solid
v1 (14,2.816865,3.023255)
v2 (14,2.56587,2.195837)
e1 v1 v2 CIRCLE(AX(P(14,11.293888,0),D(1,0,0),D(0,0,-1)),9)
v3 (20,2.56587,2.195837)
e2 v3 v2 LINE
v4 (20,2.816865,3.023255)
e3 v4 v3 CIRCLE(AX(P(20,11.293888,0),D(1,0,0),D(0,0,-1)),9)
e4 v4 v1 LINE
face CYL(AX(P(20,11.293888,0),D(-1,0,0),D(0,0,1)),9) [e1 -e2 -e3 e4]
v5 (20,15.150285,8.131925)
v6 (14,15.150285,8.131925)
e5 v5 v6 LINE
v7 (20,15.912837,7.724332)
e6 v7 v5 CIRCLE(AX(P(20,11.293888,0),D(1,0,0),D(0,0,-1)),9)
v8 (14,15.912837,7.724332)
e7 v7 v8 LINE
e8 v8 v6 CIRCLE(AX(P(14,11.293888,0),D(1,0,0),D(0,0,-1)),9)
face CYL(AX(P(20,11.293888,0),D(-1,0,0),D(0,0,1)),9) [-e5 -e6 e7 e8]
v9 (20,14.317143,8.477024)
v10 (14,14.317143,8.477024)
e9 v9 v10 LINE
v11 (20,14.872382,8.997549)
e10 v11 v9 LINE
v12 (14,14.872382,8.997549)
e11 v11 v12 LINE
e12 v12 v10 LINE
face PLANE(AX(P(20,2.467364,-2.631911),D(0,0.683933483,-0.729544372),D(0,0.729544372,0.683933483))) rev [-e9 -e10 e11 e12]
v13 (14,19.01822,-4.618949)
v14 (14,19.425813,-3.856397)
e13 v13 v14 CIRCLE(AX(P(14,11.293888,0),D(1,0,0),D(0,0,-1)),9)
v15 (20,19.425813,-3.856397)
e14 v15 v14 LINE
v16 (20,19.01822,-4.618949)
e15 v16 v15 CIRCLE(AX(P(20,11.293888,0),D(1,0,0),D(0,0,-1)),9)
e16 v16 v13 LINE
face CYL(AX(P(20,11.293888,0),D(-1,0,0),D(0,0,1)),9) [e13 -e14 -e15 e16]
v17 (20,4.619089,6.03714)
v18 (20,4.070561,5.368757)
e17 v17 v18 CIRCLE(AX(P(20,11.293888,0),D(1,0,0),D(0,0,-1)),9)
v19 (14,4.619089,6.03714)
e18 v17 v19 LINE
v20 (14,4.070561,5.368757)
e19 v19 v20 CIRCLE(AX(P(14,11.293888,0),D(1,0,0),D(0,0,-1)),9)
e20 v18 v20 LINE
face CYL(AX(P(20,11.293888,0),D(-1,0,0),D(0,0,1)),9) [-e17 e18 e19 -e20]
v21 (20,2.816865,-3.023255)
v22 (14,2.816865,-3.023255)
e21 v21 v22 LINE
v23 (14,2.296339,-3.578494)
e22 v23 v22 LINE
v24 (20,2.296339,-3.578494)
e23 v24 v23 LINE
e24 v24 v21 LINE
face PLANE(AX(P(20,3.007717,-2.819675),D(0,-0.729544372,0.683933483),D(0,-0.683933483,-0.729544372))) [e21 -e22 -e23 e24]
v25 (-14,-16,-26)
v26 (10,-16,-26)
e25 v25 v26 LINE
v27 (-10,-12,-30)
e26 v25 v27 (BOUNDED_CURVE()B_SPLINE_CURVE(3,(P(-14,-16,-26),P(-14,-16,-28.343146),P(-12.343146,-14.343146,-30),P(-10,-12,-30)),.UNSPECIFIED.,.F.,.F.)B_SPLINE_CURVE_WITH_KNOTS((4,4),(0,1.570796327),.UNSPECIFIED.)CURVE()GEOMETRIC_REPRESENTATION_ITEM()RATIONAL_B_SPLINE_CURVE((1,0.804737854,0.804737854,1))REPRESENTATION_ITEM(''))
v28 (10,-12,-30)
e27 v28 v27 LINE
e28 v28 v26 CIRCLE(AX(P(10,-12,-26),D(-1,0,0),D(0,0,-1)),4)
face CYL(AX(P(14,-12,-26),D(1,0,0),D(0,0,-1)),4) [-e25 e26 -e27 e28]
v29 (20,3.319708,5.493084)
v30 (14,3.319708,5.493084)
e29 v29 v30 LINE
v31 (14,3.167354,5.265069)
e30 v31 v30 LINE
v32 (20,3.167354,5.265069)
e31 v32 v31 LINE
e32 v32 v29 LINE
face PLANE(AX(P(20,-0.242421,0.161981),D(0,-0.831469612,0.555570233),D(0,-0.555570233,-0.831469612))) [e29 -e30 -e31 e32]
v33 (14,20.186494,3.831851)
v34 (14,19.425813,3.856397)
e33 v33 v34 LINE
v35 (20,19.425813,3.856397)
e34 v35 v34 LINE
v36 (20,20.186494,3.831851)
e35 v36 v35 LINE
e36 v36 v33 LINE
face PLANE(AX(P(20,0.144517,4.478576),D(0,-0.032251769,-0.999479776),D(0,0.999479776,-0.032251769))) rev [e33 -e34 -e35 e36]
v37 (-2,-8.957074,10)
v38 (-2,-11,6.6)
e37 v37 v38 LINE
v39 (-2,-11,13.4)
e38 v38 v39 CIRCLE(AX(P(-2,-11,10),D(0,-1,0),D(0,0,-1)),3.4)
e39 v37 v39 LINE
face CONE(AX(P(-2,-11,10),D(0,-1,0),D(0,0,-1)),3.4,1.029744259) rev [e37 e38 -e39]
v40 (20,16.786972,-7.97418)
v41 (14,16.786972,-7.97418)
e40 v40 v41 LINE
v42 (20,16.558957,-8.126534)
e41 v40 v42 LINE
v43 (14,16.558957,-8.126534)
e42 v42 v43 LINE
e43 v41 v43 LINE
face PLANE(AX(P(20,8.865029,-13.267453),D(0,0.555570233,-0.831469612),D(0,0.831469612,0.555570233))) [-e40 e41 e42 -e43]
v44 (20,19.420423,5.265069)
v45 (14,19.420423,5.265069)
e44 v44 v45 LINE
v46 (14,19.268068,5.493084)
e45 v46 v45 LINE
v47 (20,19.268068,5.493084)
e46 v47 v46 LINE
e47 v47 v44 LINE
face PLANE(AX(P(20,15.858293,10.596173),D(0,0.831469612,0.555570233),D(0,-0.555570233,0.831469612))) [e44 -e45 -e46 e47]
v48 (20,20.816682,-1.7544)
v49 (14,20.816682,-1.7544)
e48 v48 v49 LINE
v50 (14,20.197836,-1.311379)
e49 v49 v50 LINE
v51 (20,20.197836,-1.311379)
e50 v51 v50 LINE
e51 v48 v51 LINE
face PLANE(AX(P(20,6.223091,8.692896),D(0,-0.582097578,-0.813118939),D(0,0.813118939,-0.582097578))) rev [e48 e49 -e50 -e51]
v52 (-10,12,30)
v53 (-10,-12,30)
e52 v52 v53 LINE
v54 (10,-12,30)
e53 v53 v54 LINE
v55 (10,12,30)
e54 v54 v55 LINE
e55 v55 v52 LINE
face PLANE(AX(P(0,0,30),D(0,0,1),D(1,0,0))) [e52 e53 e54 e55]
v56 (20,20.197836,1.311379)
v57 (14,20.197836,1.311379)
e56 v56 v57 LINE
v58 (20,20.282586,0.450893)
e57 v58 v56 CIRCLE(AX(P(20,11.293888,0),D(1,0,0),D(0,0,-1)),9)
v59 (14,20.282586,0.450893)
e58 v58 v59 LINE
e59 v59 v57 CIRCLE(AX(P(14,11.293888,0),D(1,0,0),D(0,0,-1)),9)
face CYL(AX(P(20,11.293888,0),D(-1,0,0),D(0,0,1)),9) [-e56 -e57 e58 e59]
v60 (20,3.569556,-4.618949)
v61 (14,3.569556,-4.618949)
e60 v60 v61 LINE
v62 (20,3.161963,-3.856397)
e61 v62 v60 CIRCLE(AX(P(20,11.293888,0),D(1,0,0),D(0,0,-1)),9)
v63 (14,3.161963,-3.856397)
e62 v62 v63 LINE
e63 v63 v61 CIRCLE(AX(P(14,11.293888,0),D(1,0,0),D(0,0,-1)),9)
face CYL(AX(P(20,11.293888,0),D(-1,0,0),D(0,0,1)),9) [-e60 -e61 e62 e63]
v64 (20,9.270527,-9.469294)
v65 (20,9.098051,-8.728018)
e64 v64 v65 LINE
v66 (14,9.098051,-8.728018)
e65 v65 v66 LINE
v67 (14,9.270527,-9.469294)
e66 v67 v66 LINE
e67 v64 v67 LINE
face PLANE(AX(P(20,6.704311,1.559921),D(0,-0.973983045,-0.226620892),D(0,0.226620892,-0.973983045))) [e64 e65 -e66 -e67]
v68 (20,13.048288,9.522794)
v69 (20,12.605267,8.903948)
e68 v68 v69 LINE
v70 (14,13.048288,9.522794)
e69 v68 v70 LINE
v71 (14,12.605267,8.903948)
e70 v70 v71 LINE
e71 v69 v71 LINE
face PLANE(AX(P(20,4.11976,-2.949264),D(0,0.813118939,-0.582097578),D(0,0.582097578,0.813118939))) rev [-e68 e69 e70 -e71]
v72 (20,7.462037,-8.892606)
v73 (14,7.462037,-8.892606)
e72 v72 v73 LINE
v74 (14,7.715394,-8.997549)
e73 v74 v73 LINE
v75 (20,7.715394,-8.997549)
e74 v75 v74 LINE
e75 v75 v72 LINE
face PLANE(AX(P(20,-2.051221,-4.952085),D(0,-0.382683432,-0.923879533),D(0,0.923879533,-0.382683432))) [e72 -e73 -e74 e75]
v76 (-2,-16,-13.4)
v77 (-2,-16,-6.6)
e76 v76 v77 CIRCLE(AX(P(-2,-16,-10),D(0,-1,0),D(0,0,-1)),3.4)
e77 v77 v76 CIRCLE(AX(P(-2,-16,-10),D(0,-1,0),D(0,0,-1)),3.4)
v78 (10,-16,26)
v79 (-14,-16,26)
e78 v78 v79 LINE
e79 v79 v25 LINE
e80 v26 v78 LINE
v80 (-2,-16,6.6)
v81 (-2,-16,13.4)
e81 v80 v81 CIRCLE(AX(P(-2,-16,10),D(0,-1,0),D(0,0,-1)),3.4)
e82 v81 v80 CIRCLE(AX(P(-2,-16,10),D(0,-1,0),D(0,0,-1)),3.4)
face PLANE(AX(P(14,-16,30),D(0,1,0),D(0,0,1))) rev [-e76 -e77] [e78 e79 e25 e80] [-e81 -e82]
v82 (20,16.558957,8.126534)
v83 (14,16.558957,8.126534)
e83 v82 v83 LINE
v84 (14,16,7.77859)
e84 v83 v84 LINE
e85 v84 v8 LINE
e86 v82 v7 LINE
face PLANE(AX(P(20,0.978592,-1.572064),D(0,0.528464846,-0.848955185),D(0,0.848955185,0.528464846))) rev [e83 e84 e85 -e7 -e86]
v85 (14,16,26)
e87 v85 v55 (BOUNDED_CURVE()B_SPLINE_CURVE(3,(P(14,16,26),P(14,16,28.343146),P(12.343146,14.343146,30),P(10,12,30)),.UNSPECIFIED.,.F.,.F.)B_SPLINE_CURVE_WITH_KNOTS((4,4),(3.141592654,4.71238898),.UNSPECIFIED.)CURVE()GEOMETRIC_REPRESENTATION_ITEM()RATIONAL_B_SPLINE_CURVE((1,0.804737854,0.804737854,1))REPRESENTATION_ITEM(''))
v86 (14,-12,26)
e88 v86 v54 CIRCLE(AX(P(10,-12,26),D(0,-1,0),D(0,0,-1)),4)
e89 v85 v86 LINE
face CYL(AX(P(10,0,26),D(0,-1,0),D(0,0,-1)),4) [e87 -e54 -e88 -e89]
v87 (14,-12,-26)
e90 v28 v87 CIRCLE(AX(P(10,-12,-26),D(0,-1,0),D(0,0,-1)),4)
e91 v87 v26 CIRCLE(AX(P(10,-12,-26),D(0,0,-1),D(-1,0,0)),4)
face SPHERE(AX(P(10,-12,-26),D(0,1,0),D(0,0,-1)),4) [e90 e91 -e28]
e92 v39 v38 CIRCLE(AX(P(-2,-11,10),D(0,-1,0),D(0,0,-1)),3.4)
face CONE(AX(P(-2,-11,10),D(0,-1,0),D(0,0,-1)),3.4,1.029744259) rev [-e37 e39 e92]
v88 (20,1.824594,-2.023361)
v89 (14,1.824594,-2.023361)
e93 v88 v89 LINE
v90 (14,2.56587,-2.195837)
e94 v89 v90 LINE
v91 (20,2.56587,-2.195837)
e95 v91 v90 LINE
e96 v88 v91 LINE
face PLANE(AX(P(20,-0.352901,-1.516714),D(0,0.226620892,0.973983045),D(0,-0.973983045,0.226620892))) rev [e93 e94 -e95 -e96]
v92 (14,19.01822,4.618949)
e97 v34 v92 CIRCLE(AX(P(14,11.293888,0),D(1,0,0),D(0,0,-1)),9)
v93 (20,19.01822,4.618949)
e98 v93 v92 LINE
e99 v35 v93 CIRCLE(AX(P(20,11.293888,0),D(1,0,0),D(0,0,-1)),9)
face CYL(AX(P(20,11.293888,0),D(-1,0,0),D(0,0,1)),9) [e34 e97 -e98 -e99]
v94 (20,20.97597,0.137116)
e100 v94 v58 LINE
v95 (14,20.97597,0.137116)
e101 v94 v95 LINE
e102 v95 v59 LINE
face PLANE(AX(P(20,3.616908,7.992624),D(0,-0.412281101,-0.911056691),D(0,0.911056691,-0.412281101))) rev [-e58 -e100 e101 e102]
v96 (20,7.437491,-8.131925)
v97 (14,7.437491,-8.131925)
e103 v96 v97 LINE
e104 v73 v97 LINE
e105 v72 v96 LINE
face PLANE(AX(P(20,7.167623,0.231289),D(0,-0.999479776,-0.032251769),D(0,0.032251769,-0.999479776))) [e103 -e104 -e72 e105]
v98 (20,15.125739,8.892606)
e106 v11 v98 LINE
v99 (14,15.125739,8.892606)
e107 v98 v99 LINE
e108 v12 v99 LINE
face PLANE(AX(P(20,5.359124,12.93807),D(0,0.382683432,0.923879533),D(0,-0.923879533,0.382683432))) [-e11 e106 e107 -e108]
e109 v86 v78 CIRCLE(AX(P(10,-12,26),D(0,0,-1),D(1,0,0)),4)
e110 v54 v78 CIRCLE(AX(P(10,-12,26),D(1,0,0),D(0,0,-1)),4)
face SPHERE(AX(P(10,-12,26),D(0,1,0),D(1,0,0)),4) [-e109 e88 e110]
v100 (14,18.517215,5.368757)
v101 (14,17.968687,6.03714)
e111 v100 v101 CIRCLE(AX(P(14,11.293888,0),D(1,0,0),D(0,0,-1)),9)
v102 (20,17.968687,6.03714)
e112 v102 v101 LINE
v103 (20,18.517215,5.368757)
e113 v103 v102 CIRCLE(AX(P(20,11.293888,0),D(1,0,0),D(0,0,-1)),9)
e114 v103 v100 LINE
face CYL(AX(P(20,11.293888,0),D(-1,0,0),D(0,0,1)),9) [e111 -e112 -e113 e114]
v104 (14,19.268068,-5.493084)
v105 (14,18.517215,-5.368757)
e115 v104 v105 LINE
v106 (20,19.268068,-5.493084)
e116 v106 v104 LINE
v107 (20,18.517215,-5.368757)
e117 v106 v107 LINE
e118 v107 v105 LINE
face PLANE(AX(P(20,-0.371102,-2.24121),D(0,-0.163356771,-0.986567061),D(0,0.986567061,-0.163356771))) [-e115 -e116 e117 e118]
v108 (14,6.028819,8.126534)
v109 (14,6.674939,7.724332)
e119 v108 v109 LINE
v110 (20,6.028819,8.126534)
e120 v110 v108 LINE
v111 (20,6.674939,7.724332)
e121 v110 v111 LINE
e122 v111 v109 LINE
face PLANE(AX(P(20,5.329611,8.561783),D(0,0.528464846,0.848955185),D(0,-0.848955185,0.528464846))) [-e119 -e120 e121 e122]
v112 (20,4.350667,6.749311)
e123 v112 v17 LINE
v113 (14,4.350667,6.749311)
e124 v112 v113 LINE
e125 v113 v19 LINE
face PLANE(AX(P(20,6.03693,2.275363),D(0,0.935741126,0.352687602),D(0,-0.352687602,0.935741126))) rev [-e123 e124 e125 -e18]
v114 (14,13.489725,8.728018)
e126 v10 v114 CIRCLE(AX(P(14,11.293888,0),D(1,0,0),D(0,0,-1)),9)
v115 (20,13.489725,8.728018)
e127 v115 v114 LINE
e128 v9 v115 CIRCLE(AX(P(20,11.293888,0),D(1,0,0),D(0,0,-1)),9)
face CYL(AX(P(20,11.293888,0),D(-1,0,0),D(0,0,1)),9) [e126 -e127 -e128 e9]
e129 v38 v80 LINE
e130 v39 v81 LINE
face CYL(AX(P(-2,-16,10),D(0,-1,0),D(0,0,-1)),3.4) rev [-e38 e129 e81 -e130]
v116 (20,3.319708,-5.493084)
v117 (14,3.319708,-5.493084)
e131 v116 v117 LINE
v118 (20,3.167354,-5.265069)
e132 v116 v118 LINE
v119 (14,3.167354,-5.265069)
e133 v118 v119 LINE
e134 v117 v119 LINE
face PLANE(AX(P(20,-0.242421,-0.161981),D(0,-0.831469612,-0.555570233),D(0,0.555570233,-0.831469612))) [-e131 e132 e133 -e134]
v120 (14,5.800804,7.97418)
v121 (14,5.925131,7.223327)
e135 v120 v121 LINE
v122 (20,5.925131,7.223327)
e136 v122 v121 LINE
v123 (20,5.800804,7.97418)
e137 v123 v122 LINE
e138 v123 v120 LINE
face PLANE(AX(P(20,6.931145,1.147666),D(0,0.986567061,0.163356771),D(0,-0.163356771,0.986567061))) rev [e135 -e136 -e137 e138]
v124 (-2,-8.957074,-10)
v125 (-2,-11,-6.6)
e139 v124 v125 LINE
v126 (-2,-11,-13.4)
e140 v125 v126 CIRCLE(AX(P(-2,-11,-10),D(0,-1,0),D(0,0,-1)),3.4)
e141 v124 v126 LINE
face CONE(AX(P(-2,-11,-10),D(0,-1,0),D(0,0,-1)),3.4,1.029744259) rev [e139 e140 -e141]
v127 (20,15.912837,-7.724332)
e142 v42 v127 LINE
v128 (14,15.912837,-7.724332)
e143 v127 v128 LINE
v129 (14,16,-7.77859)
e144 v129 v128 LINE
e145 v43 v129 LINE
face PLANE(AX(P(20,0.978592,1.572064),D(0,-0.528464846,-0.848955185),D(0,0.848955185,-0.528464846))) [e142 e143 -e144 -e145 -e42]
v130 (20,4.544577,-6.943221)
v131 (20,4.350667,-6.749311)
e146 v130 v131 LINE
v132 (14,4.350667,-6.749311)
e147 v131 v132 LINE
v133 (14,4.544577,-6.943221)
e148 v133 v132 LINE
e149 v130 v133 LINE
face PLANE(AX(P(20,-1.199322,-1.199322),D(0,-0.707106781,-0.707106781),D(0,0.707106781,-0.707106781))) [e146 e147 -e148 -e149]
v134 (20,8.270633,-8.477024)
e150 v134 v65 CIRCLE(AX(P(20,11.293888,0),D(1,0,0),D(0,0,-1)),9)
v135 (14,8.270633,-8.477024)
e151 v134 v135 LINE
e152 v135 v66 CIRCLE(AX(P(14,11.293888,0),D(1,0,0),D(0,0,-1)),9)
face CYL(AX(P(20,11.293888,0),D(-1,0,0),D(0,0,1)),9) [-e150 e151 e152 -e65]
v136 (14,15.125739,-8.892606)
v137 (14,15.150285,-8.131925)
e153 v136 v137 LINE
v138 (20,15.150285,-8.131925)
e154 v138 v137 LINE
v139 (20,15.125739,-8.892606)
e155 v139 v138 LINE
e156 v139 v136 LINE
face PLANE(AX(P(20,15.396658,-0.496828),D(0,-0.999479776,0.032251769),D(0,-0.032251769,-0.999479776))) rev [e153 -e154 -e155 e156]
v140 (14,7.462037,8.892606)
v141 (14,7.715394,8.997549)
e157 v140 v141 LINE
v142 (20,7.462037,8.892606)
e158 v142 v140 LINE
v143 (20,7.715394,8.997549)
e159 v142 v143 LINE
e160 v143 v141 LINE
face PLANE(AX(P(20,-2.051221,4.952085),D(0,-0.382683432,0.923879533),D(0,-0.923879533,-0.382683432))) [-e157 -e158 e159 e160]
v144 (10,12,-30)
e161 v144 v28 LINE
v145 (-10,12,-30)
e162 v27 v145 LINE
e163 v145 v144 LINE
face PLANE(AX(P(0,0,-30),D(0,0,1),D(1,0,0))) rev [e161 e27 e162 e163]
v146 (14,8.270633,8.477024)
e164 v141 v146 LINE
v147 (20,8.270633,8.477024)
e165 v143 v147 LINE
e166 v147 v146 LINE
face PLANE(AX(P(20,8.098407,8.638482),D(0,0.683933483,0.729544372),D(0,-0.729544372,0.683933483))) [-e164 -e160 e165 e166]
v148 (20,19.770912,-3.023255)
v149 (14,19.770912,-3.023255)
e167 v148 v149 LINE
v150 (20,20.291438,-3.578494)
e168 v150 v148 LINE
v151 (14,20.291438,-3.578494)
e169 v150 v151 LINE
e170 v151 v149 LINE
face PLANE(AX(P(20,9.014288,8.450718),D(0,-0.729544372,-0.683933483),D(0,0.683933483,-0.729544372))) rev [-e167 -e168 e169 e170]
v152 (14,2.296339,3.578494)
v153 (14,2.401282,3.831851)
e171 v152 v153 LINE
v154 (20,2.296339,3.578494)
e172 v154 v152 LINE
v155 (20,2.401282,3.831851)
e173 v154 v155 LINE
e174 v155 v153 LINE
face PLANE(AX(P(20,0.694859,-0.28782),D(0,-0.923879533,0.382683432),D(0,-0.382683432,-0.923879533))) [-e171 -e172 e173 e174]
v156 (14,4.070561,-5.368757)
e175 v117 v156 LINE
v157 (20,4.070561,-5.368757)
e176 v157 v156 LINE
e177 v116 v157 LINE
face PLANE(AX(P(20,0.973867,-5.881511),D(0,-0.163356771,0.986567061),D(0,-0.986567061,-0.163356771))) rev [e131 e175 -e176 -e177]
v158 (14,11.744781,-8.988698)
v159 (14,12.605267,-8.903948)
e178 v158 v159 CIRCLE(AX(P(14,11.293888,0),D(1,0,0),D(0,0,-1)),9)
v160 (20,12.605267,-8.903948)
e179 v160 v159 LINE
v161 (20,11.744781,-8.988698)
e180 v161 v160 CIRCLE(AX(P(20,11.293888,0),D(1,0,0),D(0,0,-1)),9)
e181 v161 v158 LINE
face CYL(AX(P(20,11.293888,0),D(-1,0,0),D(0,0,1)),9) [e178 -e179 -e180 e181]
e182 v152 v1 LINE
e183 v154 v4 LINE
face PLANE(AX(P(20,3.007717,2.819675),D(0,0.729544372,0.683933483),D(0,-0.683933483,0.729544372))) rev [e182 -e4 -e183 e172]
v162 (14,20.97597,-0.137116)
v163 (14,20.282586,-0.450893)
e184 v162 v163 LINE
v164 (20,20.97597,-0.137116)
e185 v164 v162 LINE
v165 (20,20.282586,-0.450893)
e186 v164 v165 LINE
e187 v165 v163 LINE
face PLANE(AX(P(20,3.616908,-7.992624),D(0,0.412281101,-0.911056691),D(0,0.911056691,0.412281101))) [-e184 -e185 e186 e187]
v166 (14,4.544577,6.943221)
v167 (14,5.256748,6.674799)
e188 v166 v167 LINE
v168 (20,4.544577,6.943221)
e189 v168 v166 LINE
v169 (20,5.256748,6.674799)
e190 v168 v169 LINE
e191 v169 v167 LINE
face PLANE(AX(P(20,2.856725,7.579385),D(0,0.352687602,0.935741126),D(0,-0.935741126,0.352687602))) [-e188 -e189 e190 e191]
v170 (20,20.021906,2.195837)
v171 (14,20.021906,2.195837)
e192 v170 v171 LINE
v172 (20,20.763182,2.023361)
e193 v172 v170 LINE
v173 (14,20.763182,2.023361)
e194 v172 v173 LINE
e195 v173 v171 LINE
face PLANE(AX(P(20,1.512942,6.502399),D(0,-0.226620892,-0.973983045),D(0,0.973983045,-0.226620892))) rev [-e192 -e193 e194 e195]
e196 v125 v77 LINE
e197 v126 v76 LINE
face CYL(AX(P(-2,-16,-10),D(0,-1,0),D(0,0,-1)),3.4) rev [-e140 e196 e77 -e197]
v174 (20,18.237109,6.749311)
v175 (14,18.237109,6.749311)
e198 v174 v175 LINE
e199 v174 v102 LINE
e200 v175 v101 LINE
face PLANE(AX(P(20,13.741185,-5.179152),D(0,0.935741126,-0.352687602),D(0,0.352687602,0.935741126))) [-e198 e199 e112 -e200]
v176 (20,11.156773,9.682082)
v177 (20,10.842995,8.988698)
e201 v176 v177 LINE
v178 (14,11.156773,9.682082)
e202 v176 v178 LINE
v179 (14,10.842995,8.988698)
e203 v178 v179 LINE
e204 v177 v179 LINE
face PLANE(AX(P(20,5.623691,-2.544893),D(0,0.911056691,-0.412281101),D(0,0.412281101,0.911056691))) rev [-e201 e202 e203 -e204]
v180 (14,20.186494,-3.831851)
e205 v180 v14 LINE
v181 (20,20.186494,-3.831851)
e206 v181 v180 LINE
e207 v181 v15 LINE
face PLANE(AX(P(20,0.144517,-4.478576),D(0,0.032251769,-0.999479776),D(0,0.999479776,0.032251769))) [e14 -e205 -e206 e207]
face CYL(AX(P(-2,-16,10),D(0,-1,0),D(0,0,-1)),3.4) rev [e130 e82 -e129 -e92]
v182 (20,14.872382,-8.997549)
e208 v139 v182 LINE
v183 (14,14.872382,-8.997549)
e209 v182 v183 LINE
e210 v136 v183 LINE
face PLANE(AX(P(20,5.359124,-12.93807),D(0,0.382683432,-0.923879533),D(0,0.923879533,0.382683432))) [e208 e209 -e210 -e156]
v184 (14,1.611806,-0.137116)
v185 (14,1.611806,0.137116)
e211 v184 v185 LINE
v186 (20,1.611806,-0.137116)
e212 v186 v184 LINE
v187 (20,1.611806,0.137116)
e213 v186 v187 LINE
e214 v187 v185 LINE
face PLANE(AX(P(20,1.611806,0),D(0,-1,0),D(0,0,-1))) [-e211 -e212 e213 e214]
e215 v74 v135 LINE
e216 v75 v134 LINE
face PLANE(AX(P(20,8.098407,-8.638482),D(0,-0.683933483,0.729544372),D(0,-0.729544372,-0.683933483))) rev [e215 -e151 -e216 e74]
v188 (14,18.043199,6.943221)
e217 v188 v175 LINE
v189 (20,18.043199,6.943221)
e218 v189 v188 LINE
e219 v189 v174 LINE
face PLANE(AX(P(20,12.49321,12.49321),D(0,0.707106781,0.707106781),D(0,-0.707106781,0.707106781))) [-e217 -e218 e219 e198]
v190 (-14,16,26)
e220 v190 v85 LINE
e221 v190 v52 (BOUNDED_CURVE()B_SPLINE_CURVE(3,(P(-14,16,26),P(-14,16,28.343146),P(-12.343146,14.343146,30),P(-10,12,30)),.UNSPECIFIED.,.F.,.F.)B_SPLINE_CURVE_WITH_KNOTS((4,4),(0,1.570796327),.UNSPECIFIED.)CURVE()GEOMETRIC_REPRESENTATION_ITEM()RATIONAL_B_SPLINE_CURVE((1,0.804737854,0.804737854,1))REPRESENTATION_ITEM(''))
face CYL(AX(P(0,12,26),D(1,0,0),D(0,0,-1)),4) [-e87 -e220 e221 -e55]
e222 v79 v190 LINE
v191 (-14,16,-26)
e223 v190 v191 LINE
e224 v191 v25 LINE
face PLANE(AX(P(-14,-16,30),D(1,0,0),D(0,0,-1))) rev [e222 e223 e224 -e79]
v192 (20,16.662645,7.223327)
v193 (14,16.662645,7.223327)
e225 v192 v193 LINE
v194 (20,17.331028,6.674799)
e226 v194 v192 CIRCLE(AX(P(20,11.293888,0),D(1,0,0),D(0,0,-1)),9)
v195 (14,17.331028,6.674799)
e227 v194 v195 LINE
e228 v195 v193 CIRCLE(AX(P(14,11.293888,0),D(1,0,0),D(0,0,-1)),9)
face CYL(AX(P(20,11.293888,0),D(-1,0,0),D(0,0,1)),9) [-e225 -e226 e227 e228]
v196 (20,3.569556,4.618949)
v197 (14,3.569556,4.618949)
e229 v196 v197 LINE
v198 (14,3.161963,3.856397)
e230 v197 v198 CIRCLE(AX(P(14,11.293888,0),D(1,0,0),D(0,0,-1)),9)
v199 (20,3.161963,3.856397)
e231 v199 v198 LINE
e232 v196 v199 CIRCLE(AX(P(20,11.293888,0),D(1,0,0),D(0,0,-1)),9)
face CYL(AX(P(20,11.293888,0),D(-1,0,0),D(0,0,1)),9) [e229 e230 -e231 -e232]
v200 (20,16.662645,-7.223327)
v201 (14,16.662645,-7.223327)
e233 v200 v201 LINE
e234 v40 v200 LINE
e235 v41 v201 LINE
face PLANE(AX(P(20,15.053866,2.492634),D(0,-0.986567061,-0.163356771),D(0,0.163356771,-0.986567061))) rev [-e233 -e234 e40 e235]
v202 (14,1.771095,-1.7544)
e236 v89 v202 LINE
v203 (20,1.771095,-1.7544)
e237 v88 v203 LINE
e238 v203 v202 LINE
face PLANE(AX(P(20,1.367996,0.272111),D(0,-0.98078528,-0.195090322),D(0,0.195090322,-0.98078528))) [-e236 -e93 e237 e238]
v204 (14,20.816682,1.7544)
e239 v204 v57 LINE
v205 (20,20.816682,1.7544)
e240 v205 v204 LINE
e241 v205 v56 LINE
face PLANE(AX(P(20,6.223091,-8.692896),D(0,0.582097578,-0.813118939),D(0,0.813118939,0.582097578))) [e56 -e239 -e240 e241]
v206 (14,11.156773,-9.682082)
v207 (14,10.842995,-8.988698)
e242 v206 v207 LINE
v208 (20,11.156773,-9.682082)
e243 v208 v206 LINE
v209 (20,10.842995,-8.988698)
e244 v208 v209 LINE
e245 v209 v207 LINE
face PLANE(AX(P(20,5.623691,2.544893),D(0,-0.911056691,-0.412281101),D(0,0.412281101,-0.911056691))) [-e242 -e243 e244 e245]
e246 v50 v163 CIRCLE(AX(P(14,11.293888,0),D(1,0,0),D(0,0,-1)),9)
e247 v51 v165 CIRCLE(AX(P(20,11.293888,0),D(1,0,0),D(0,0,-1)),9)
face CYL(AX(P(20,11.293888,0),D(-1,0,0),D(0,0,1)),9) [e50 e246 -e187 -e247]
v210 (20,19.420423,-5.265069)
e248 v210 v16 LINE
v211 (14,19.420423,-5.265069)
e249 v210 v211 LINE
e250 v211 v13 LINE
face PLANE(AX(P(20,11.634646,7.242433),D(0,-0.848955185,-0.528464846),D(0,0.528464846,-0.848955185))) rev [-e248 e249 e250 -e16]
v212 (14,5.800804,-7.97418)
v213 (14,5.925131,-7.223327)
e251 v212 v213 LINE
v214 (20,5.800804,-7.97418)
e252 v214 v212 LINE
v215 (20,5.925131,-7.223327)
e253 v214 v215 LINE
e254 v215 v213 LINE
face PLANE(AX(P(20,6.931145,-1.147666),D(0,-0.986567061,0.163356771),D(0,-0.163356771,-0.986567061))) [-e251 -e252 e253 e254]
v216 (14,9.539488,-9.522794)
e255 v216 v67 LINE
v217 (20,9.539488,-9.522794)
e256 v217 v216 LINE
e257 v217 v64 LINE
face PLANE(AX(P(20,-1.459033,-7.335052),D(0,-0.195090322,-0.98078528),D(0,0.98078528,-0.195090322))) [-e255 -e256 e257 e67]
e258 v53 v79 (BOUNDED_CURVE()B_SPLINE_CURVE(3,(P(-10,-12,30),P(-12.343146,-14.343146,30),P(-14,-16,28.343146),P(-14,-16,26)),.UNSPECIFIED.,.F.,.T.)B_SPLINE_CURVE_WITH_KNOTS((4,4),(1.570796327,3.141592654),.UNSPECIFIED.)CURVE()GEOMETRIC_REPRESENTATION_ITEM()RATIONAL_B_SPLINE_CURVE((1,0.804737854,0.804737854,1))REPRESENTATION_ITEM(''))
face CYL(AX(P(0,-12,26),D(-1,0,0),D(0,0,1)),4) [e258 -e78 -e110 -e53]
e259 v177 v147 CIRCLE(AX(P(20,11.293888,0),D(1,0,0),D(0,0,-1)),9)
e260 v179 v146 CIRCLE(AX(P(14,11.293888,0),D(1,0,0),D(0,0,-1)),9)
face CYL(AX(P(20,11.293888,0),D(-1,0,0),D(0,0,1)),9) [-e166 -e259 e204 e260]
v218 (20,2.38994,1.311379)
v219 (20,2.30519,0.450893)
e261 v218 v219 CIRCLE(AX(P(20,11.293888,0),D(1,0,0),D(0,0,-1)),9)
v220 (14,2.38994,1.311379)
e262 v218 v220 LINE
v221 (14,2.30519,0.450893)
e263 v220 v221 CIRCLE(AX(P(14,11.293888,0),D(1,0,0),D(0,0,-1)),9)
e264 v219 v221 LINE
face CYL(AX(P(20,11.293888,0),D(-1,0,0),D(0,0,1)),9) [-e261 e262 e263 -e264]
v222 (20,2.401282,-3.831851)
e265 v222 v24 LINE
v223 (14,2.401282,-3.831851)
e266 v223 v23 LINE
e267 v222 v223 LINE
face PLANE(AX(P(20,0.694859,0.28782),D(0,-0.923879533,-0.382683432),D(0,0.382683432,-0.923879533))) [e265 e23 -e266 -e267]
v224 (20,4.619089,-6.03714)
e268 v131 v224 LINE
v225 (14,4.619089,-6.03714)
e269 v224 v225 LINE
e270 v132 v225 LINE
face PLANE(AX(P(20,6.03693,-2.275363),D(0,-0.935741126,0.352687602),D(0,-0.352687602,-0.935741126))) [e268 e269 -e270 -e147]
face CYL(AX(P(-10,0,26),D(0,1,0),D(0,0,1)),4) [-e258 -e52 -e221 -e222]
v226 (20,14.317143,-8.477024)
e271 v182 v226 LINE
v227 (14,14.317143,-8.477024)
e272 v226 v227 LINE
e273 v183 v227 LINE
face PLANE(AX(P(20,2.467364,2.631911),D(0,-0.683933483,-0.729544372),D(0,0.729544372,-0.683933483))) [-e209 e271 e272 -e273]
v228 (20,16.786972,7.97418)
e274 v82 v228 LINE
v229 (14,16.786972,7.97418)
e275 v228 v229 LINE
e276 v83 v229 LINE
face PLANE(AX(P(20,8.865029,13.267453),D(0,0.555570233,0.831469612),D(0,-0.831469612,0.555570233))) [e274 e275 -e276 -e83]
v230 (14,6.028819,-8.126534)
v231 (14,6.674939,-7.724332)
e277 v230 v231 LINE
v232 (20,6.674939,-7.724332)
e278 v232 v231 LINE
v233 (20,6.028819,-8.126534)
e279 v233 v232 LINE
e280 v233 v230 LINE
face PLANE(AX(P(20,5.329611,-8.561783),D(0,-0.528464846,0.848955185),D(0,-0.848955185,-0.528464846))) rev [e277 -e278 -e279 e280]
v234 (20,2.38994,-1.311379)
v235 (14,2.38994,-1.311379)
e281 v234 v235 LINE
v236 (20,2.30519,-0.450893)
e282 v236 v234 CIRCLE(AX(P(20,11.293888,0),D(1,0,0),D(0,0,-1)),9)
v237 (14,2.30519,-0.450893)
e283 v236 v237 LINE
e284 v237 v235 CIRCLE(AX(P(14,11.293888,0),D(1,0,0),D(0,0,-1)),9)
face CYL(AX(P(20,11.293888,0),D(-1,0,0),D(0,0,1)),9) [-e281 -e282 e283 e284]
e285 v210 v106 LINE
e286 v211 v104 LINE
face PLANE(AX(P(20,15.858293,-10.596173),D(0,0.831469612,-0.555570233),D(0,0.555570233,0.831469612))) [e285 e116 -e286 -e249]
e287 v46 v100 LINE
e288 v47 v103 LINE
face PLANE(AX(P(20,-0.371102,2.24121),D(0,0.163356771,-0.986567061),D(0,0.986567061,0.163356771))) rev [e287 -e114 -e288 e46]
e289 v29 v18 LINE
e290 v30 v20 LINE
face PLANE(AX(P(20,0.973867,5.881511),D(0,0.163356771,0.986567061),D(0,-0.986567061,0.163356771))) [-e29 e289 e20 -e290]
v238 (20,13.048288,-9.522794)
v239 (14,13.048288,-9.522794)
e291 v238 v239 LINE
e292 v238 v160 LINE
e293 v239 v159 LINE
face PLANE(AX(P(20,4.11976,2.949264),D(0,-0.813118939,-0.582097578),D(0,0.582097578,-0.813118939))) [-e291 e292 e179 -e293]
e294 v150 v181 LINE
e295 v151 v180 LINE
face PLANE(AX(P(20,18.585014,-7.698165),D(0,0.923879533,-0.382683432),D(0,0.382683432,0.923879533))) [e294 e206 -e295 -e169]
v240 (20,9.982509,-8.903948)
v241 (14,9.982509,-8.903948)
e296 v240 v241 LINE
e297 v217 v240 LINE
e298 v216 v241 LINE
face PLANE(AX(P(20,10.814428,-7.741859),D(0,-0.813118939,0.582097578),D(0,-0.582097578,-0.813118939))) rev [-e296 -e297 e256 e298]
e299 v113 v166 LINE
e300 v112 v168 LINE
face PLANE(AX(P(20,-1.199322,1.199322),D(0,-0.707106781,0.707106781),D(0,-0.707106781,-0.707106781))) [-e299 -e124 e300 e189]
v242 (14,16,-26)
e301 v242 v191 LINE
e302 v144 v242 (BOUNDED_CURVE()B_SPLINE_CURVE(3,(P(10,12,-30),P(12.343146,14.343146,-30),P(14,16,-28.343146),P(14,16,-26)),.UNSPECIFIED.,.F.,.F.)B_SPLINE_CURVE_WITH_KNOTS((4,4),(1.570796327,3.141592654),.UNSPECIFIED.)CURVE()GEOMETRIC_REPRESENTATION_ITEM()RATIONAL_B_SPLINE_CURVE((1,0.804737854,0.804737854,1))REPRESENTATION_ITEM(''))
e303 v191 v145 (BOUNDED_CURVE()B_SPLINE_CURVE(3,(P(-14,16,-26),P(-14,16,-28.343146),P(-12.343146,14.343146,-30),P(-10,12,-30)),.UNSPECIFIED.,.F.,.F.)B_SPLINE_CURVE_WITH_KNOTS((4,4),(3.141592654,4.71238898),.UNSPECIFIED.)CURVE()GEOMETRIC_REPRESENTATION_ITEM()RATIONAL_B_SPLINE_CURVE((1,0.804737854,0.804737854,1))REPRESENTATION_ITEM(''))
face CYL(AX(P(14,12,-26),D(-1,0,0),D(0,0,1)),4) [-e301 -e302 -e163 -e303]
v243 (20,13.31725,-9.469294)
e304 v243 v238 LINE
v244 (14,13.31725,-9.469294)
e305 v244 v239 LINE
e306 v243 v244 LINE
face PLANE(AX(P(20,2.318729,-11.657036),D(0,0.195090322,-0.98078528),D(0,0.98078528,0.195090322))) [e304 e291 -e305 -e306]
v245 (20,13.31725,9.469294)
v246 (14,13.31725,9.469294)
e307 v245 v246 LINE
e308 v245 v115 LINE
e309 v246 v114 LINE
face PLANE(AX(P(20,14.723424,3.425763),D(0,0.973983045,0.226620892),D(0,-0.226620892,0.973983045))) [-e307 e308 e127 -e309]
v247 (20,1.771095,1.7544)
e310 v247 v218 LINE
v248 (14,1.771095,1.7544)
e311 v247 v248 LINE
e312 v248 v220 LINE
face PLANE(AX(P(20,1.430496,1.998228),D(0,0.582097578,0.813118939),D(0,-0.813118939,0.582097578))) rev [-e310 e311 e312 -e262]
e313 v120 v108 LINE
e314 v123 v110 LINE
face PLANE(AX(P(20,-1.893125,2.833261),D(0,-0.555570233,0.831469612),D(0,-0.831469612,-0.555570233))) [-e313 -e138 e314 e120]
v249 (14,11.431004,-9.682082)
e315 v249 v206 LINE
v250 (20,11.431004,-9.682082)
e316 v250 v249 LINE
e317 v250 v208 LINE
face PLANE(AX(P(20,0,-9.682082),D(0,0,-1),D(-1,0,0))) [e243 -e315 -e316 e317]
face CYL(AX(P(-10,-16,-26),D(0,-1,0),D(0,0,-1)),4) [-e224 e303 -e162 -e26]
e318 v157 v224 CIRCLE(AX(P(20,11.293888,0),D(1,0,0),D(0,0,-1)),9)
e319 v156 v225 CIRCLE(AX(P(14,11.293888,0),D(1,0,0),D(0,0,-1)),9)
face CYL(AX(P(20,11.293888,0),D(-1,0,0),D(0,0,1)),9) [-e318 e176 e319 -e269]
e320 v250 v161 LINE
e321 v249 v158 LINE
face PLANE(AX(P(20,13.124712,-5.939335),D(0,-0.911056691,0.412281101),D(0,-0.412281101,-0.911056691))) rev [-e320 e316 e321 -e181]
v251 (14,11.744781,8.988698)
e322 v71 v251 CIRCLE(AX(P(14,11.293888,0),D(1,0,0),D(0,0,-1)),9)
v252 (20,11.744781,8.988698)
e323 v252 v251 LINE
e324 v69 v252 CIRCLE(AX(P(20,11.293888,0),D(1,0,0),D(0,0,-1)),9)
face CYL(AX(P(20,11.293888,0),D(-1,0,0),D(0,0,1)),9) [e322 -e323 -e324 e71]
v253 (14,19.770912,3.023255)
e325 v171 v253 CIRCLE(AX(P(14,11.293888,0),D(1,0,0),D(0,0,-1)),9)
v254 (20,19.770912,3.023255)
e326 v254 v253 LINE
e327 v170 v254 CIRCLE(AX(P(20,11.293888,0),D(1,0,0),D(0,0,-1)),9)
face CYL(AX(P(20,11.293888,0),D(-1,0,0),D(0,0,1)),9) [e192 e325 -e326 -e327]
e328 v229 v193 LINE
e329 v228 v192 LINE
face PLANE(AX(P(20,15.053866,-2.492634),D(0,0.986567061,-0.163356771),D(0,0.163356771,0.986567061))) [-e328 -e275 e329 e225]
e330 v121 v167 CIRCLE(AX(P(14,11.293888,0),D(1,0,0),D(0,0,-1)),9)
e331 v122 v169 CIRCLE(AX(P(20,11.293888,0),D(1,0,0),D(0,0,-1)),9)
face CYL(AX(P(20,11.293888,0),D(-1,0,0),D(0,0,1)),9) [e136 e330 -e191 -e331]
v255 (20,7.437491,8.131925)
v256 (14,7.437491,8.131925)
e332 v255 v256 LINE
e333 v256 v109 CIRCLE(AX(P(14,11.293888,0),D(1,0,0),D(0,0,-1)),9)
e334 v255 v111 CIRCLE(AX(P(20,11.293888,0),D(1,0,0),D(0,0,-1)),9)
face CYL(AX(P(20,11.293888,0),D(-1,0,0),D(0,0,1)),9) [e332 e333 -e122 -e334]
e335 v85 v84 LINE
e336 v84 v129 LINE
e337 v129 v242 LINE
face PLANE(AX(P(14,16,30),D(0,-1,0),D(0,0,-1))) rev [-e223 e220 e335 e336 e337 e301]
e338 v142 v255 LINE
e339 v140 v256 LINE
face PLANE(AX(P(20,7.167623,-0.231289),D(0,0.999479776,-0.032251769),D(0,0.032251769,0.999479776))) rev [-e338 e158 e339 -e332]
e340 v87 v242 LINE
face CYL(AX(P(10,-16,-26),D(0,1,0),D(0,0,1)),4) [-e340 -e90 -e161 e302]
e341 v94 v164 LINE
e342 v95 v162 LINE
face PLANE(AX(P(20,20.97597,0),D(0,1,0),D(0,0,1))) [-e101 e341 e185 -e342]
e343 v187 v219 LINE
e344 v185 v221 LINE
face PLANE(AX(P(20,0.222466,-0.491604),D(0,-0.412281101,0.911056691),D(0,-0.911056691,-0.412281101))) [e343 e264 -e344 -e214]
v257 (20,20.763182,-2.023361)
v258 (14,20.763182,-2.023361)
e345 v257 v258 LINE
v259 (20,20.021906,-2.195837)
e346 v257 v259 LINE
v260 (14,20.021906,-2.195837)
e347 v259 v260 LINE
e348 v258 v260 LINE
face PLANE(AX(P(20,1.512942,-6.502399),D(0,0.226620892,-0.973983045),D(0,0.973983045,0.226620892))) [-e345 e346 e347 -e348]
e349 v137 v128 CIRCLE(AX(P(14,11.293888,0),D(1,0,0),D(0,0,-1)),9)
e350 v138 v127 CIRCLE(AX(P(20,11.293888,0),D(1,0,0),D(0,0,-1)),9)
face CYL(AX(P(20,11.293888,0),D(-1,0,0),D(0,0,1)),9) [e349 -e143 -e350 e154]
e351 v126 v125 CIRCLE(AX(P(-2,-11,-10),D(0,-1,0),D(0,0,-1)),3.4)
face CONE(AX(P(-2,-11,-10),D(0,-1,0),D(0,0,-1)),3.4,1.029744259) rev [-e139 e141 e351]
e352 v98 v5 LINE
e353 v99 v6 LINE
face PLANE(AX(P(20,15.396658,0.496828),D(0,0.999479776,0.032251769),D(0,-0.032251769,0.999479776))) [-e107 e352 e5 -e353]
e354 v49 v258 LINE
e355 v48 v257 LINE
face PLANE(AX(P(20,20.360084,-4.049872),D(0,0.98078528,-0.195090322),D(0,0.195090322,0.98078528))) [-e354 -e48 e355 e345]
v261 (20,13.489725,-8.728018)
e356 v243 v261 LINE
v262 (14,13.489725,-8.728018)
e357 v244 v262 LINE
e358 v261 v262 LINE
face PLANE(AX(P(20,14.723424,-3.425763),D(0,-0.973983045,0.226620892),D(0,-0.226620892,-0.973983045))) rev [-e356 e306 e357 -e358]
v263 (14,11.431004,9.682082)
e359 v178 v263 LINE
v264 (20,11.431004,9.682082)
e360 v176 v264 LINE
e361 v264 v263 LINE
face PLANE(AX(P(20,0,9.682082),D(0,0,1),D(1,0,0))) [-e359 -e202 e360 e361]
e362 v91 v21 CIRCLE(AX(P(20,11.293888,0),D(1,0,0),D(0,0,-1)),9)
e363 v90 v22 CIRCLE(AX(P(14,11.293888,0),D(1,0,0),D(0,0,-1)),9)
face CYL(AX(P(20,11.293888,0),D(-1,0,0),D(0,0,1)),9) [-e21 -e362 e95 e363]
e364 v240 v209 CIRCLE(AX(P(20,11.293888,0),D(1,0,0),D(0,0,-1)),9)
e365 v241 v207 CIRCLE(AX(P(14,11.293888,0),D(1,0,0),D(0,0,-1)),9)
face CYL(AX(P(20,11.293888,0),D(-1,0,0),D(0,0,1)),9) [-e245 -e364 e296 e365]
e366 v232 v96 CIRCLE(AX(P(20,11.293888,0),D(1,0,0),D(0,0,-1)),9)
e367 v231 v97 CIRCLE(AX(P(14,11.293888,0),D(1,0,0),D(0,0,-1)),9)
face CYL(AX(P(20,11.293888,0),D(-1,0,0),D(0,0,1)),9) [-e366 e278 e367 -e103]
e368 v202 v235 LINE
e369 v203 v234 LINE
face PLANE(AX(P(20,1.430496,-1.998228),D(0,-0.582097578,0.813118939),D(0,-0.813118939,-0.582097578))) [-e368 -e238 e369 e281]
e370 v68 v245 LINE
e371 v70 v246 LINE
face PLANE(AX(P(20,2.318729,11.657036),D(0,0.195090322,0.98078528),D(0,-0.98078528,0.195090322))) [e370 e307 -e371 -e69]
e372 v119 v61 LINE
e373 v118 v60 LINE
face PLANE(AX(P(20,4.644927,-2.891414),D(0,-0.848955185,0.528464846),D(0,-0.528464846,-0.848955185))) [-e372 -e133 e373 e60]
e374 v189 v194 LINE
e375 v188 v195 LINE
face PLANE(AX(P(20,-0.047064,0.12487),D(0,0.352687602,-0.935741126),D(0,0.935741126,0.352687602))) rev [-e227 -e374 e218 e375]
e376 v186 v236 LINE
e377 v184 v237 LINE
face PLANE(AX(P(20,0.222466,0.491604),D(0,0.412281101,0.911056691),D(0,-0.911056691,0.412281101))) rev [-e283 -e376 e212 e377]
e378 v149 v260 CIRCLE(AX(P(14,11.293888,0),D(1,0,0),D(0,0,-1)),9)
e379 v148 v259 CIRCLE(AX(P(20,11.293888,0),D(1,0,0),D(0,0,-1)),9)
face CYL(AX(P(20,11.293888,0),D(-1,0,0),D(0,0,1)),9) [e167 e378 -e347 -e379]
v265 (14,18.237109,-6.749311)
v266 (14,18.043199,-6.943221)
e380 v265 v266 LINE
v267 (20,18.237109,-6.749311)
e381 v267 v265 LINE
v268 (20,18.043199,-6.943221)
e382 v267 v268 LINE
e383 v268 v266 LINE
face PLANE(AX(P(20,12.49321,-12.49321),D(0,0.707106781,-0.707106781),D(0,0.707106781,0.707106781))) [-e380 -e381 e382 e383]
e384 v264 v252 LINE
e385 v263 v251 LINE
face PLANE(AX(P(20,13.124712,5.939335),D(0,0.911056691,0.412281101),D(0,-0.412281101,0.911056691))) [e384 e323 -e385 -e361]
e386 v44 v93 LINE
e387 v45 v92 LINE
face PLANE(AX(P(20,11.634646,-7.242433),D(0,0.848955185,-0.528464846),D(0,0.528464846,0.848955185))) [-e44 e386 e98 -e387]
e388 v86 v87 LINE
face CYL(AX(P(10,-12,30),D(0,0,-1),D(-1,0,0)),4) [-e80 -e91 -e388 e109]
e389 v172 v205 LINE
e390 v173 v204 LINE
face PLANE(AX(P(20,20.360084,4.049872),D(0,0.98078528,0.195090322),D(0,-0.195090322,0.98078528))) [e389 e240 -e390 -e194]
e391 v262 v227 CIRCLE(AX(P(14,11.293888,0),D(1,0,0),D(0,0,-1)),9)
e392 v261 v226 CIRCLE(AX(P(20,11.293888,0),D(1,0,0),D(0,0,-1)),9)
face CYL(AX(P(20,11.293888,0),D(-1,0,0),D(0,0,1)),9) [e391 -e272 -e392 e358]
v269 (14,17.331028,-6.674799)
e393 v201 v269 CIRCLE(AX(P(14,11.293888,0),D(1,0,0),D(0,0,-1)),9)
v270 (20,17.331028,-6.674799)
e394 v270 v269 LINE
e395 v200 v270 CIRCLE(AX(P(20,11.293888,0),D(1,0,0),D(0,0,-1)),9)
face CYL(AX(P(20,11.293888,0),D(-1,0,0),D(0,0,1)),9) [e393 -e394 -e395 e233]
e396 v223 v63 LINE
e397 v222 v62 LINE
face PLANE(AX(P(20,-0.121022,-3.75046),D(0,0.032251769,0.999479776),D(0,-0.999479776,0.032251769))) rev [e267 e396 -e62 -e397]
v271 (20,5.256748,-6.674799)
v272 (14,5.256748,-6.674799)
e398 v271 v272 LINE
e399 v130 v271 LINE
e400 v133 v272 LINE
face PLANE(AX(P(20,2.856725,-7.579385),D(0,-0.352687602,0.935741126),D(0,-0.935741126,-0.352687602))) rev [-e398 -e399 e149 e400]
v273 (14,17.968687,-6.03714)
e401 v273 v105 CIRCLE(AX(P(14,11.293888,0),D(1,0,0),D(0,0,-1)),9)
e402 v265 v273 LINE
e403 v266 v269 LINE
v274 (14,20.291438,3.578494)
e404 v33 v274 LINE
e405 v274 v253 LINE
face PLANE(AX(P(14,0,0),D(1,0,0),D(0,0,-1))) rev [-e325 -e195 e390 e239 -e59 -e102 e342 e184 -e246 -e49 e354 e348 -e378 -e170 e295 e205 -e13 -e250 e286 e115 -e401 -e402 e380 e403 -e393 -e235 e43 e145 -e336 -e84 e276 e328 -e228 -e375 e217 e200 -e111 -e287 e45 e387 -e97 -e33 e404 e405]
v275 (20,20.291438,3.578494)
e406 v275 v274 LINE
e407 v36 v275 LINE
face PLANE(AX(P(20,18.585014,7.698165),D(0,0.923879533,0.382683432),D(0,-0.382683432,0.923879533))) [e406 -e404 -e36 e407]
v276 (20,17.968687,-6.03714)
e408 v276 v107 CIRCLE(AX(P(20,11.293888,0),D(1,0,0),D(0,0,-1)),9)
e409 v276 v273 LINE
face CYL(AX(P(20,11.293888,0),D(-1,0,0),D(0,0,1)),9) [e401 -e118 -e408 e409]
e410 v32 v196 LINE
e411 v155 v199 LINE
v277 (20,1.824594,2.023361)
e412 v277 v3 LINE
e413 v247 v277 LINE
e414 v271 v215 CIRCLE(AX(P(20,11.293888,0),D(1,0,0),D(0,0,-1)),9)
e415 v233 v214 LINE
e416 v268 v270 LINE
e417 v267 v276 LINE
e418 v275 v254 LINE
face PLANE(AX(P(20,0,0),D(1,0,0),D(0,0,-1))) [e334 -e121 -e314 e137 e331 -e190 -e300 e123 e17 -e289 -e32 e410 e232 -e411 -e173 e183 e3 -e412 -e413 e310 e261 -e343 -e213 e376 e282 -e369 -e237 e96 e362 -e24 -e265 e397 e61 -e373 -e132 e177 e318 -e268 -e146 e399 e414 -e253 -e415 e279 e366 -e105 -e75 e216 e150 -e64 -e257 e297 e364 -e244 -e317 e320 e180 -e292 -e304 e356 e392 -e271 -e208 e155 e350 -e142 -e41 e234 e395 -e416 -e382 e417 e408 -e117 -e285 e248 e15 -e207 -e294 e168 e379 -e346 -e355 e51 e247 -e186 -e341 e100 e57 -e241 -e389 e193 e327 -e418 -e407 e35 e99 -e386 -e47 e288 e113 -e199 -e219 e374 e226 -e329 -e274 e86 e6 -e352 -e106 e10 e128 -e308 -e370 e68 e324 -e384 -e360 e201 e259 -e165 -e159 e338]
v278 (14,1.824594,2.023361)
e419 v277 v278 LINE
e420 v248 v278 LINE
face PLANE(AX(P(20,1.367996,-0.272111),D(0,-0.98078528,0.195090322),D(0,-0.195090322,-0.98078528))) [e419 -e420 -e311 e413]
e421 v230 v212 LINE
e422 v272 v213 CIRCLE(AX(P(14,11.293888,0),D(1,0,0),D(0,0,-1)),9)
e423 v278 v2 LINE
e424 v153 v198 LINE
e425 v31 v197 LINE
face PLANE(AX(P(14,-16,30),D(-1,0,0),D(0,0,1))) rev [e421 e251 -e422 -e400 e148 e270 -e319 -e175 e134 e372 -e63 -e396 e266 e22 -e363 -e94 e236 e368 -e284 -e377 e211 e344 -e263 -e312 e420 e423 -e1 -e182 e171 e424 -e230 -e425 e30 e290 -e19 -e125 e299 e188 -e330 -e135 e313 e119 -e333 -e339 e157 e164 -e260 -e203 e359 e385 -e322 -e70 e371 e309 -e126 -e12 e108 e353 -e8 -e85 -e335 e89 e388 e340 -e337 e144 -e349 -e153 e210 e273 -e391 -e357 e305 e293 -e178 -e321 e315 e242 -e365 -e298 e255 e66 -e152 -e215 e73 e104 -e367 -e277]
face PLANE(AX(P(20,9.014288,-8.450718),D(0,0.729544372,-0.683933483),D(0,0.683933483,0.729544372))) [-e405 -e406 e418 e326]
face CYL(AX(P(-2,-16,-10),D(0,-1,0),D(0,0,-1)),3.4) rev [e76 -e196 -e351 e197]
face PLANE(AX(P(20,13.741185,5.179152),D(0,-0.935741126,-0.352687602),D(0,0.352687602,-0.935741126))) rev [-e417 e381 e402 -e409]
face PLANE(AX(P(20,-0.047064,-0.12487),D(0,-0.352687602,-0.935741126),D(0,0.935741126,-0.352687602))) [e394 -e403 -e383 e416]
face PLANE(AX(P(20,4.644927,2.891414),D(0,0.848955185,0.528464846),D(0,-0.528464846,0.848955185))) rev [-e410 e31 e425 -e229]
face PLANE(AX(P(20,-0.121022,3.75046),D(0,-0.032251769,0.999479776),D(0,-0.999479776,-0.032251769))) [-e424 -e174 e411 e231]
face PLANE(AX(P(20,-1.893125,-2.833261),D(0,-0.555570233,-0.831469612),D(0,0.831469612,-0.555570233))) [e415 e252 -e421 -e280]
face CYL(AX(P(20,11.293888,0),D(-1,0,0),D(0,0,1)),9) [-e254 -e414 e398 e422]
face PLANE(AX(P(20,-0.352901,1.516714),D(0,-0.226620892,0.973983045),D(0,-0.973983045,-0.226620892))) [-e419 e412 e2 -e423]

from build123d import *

# Parameters (mm, degrees)
SKETCH1_W                   = 28
SKETCH1_H                   = 32
BOSS_EXTRUDE1_DEPTH         = 30
BOSS_EXTRUDE3_DEPTH         = 6
FILLET1_R                   = 4
TAP_DRILL_FOR_M8_TAP1_D     = 6.8
TAP_DRILL_FOR_M8_TAP1_DEPTH = 5
TAP_DRILL_FOR_M8_TAP1_TIP   = 2.042926105


with BuildPart() as part:
    # Sketch1 → Boss-Extrude1 (new, symmetric)
    with BuildSketch(Plane.XY):
        Rectangle(SKETCH1_W, SKETCH1_H)
    extrude(amount=BOSS_EXTRUDE1_DEPTH, both=True)

    # Sketch2 → Boss-Extrude3 (add)
    with BuildSketch(Plane(origin=(14, 0, 0), x_dir=(0, 0, -1), z_dir=(1, 0, 0))):
        with BuildLine():
            Line((-0.137115518, 20.975970302), (0.137115518, 20.975970302))
            Line((0.137115518, 20.975970302), (0.450893035, 20.282586335))
            ThreePointArc((0.450893035, 20.282586335), (0.882154263, 20.250550667), (1.311378777, 20.197835887))
            Line((1.311378777, 20.197835887), (1.754399647, 20.816681719))
            Line((1.754399647, 20.816681719), (2.023361412, 20.763181898))
            Line((2.023361412, 20.763181898), (2.195837279, 20.021906152))
            ThreePointArc((2.195837279, 20.021906152), (2.612562095, 19.906351149), (3.023255037, 19.77091172))
            Line((3.023255037, 19.77091172), (3.578494218, 20.291437518))
            Line((3.578494218, 20.291437518), (3.83185066, 20.186493844))
            Line((3.83185066, 20.186493844), (3.856396729, 19.425813131))
            ThreePointArc((3.856396729, 19.425813131), (4.242570631, 19.231179507), (4.618949301, 19.01822029))
            Line((4.618949301, 19.01822029), (5.265069263, 19.42042254))
            Line((5.265069263, 19.42042254), (5.493084037, 19.268067939))
            Line((5.493084037, 19.268067939), (5.368757014, 18.517214793))
            ThreePointArc((5.368757014, 18.517214793), (5.709539557, 18.250982208), (6.037139934, 17.968687106))
            Line((6.037139934, 17.968687106), (6.749310649, 18.237109402))
            Line((6.749310649, 18.237109402), (6.943221275, 18.043198777))
            Line((6.943221275, 18.043198777), (6.674798979, 17.331028062))
            ThreePointArc((6.674798979, 17.331028062), (6.95709408, 17.003427685), (7.223326666, 16.662645142))
            Line((7.223326666, 16.662645142), (7.974179812, 16.786972164))
            Line((7.974179812, 16.786972164), (8.126534413, 16.558957391))
            Line((8.126534413, 16.558957391), (7.724332162, 15.912837429))
            ThreePointArc((7.724332162, 15.912837429), (7.937291379, 15.536458759), (8.131925004, 15.150284856))
            Line((8.131925004, 15.150284856), (8.892605716, 15.125738788))
            Line((8.892605716, 15.125738788), (8.997549391, 14.872382346))
            Line((8.997549391, 14.872382346), (8.477023592, 14.317143164))
            ThreePointArc((8.477023592, 14.317143164), (8.612463022, 13.906450223), (8.728018025, 13.489725407))
            Line((8.728018025, 13.489725407), (9.46929377, 13.317249539))
            Line((9.46929377, 13.317249539), (9.522793592, 13.048287775))
            Line((9.522793592, 13.048287775), (8.90394776, 12.605266904))
            ThreePointArc((8.90394776, 12.605266904), (8.95666254, 12.17604239), (8.988698208, 11.744781162))
            Line((8.988698208, 11.744781162), (9.682082175, 11.431003646))
            Line((9.682082175, 11.431003646), (9.682082175, 11.156772609))
            Line((9.682082175, 11.156772609), (8.988698208, 10.842995093))
            ThreePointArc((8.988698208, 10.842995093), (8.95666254, 10.411733864), (8.90394776, 9.982509351))
            Line((8.90394776, 9.982509351), (9.522793592, 9.53948848))
            Line((9.522793592, 9.53948848), (9.46929377, 9.270526716))
            Line((9.46929377, 9.270526716), (8.728018025, 9.098050848))
            ThreePointArc((8.728018025, 9.098050848), (8.612463022, 8.681326032), (8.477023592, 8.270633091))
            Line((8.477023592, 8.270633091), (8.997549391, 7.715393909))
            Line((8.997549391, 7.715393909), (8.892605716, 7.462037467))
            Line((8.892605716, 7.462037467), (8.131925004, 7.437491399))
            ThreePointArc((8.131925004, 7.437491399), (7.937291379, 7.051317496), (7.724332162, 6.674938826))
            Line((7.724332162, 6.674938826), (8.126534413, 6.028818864))
            Line((8.126534413, 6.028818864), (7.974179812, 5.80080409))
            Line((7.974179812, 5.80080409), (7.223326666, 5.925131113))
            ThreePointArc((7.223326666, 5.925131113), (6.95709408, 5.58434857), (6.674798979, 5.256748193))
            Line((6.674798979, 5.256748193), (6.943221275, 4.544577478))
            Line((6.943221275, 4.544577478), (6.749310649, 4.350666852))
            Line((6.749310649, 4.350666852), (6.037139934, 4.619089148))
            ThreePointArc((6.037139934, 4.619089148), (5.709539557, 4.336794047), (5.368757014, 4.070561462))
            Line((5.368757014, 4.070561462), (5.493084037, 3.319708316))
            Line((5.493084037, 3.319708316), (5.265069263, 3.167353714))
            Line((5.265069263, 3.167353714), (4.618949301, 3.569555965))
            ThreePointArc((4.618949301, 3.569555965), (4.242570631, 3.356596748), (3.856396729, 3.161963123))
            Line((3.856396729, 3.161963123), (3.83185066, 2.401282411))
            Line((3.83185066, 2.401282411), (3.578494218, 2.296338737))
            Line((3.578494218, 2.296338737), (3.023255037, 2.816864535))
            ThreePointArc((3.023255037, 2.816864535), (2.612562095, 2.681425106), (2.195837279, 2.565870102))
            Line((2.195837279, 2.565870102), (2.023361412, 1.824594357))
            Line((2.023361412, 1.824594357), (1.754399647, 1.771094536))
            Line((1.754399647, 1.771094536), (1.311378777, 2.389940368))
            ThreePointArc((1.311378777, 2.389940368), (0.882154263, 2.337225587), (0.450893035, 2.30518992))
            Line((0.450893035, 2.30518992), (0.137115518, 1.611805952))
            Line((0.137115518, 1.611805952), (-0.137115518, 1.611805952))
            Line((-0.137115518, 1.611805952), (-0.450893035, 2.30518992))
            ThreePointArc((-0.450893035, 2.30518992), (-0.882154263, 2.337225587), (-1.311378777, 2.389940368))
            Line((-1.311378777, 2.389940368), (-1.754399647, 1.771094536))
            Line((-1.754399647, 1.771094536), (-2.023361412, 1.824594357))
            Line((-2.023361412, 1.824594357), (-2.195837279, 2.565870102))
            ThreePointArc((-2.195837279, 2.565870102), (-2.612562095, 2.681425106), (-3.023255037, 2.816864535))
            Line((-3.023255037, 2.816864535), (-3.578494218, 2.296338737))
            Line((-3.578494218, 2.296338737), (-3.83185066, 2.401282411))
            Line((-3.83185066, 2.401282411), (-3.856396729, 3.161963123))
            ThreePointArc((-3.856396729, 3.161963123), (-4.242570631, 3.356596748), (-4.618949301, 3.569555965))
            Line((-4.618949301, 3.569555965), (-5.265069263, 3.167353714))
            Line((-5.265069263, 3.167353714), (-5.493084037, 3.319708316))
            Line((-5.493084037, 3.319708316), (-5.368757014, 4.070561462))
            ThreePointArc((-5.368757014, 4.070561462), (-5.709539557, 4.336794047), (-6.037139934, 4.619089148))
            Line((-6.037139934, 4.619089148), (-6.749310649, 4.350666852))
            Line((-6.749310649, 4.350666852), (-6.943221275, 4.544577478))
            Line((-6.943221275, 4.544577478), (-6.674798979, 5.256748193))
            ThreePointArc((-6.674798979, 5.256748193), (-6.95709408, 5.58434857), (-7.223326666, 5.925131113))
            Line((-7.223326666, 5.925131113), (-7.974179812, 5.80080409))
            Line((-7.974179812, 5.80080409), (-8.126534413, 6.028818864))
            Line((-8.126534413, 6.028818864), (-7.724332162, 6.674938826))
            ThreePointArc((-7.724332162, 6.674938826), (-7.937291379, 7.051317496), (-8.131925004, 7.437491399))
            Line((-8.131925004, 7.437491399), (-8.892605716, 7.462037467))
            Line((-8.892605716, 7.462037467), (-8.997549391, 7.715393909))
            Line((-8.997549391, 7.715393909), (-8.477023592, 8.270633091))
            ThreePointArc((-8.477023592, 8.270633091), (-8.827067524, 9.538075229), (-8.988698208, 10.842995093))
            Line((-8.988698208, 10.842995093), (-9.682082175, 11.156772609))
            Line((-9.682082175, 11.156772609), (-9.682082175, 11.431003646))
            Line((-9.682082175, 11.431003646), (-8.988698208, 11.744781162))
            ThreePointArc((-8.988698208, 11.744781162), (-8.95666254, 12.17604239), (-8.90394776, 12.605266904))
            Line((-8.90394776, 12.605266904), (-9.522793592, 13.048287775))
            Line((-9.522793592, 13.048287775), (-9.46929377, 13.317249539))
            Line((-9.46929377, 13.317249539), (-8.728018025, 13.489725407))
            ThreePointArc((-8.728018025, 13.489725407), (-8.612463022, 13.906450223), (-8.477023592, 14.317143164))
            Line((-8.477023592, 14.317143164), (-8.997549391, 14.872382346))
            Line((-8.997549391, 14.872382346), (-8.892605716, 15.125738788))
            Line((-8.892605716, 15.125738788), (-8.131925004, 15.150284856))
            ThreePointArc((-8.131925004, 15.150284856), (-7.937291379, 15.536458759), (-7.724332162, 15.912837429))
            Line((-7.724332162, 15.912837429), (-8.126534413, 16.558957391))
            Line((-8.126534413, 16.558957391), (-7.974179812, 16.786972164))
            Line((-7.974179812, 16.786972164), (-7.223326666, 16.662645142))
            ThreePointArc((-7.223326666, 16.662645142), (-6.95709408, 17.003427685), (-6.674798979, 17.331028062))
            Line((-6.674798979, 17.331028062), (-6.943221275, 18.043198777))
            Line((-6.943221275, 18.043198777), (-6.749310649, 18.237109402))
            Line((-6.749310649, 18.237109402), (-6.037139934, 17.968687106))
            ThreePointArc((-6.037139934, 17.968687106), (-5.709539557, 18.250982208), (-5.368757014, 18.517214793))
            Line((-5.368757014, 18.517214793), (-5.493084037, 19.268067939))
            Line((-5.493084037, 19.268067939), (-5.265069263, 19.42042254))
            Line((-5.265069263, 19.42042254), (-4.618949301, 19.01822029))
            ThreePointArc((-4.618949301, 19.01822029), (-4.242570631, 19.231179507), (-3.856396729, 19.425813131))
            Line((-3.856396729, 19.425813131), (-3.83185066, 20.186493844))
            Line((-3.83185066, 20.186493844), (-3.578494218, 20.291437518))
            Line((-3.578494218, 20.291437518), (-3.023255037, 19.77091172))
            ThreePointArc((-3.023255037, 19.77091172), (-2.612562095, 19.906351149), (-2.195837279, 20.021906152))
            Line((-2.195837279, 20.021906152), (-2.023361412, 20.763181898))
            Line((-2.023361412, 20.763181898), (-1.754399647, 20.816681719))
            Line((-1.754399647, 20.816681719), (-1.311378777, 20.197835887))
            ThreePointArc((-1.311378777, 20.197835887), (-0.882154263, 20.250550667), (-0.450893035, 20.282586335))
            Line((-0.450893035, 20.282586335), (-0.137115518, 20.975970302))
        make_face()
    extrude(amount=BOSS_EXTRUDE3_DEPTH)

    # Fillet1
    fillet1_edges = [part.edges().sort_by_distance(p)[0] for p in [
        (14, 0, 30),
        (0, 16, 30),
        (-14, 0, 30),
        (0, 16, -30),
        (14, 0, -30),
        (0, -16, -30),
        (-14, 0, -30),
        (14, -16, 0),
        (0, -16, 30),
    ]]
    fillet(fillet1_edges, radius=FILLET1_R)

    # Tap Drill for M8 Tap1
    with Locations(Plane.XZ.offset(16)):
        with Locations((-2, 10), (-2, -10)):
            Hole(TAP_DRILL_FOR_M8_TAP1_D / 2, depth=TAP_DRILL_FOR_M8_TAP1_DEPTH)
            with Locations((0, 0, -(TAP_DRILL_FOR_M8_TAP1_DEPTH + TAP_DRILL_FOR_M8_TAP1_TIP / 2))):  # 118° drill point
                Cone(0, TAP_DRILL_FOR_M8_TAP1_D / 2, TAP_DRILL_FOR_M8_TAP1_TIP, mode=Mode.SUBTRACT)


solid = part.part
